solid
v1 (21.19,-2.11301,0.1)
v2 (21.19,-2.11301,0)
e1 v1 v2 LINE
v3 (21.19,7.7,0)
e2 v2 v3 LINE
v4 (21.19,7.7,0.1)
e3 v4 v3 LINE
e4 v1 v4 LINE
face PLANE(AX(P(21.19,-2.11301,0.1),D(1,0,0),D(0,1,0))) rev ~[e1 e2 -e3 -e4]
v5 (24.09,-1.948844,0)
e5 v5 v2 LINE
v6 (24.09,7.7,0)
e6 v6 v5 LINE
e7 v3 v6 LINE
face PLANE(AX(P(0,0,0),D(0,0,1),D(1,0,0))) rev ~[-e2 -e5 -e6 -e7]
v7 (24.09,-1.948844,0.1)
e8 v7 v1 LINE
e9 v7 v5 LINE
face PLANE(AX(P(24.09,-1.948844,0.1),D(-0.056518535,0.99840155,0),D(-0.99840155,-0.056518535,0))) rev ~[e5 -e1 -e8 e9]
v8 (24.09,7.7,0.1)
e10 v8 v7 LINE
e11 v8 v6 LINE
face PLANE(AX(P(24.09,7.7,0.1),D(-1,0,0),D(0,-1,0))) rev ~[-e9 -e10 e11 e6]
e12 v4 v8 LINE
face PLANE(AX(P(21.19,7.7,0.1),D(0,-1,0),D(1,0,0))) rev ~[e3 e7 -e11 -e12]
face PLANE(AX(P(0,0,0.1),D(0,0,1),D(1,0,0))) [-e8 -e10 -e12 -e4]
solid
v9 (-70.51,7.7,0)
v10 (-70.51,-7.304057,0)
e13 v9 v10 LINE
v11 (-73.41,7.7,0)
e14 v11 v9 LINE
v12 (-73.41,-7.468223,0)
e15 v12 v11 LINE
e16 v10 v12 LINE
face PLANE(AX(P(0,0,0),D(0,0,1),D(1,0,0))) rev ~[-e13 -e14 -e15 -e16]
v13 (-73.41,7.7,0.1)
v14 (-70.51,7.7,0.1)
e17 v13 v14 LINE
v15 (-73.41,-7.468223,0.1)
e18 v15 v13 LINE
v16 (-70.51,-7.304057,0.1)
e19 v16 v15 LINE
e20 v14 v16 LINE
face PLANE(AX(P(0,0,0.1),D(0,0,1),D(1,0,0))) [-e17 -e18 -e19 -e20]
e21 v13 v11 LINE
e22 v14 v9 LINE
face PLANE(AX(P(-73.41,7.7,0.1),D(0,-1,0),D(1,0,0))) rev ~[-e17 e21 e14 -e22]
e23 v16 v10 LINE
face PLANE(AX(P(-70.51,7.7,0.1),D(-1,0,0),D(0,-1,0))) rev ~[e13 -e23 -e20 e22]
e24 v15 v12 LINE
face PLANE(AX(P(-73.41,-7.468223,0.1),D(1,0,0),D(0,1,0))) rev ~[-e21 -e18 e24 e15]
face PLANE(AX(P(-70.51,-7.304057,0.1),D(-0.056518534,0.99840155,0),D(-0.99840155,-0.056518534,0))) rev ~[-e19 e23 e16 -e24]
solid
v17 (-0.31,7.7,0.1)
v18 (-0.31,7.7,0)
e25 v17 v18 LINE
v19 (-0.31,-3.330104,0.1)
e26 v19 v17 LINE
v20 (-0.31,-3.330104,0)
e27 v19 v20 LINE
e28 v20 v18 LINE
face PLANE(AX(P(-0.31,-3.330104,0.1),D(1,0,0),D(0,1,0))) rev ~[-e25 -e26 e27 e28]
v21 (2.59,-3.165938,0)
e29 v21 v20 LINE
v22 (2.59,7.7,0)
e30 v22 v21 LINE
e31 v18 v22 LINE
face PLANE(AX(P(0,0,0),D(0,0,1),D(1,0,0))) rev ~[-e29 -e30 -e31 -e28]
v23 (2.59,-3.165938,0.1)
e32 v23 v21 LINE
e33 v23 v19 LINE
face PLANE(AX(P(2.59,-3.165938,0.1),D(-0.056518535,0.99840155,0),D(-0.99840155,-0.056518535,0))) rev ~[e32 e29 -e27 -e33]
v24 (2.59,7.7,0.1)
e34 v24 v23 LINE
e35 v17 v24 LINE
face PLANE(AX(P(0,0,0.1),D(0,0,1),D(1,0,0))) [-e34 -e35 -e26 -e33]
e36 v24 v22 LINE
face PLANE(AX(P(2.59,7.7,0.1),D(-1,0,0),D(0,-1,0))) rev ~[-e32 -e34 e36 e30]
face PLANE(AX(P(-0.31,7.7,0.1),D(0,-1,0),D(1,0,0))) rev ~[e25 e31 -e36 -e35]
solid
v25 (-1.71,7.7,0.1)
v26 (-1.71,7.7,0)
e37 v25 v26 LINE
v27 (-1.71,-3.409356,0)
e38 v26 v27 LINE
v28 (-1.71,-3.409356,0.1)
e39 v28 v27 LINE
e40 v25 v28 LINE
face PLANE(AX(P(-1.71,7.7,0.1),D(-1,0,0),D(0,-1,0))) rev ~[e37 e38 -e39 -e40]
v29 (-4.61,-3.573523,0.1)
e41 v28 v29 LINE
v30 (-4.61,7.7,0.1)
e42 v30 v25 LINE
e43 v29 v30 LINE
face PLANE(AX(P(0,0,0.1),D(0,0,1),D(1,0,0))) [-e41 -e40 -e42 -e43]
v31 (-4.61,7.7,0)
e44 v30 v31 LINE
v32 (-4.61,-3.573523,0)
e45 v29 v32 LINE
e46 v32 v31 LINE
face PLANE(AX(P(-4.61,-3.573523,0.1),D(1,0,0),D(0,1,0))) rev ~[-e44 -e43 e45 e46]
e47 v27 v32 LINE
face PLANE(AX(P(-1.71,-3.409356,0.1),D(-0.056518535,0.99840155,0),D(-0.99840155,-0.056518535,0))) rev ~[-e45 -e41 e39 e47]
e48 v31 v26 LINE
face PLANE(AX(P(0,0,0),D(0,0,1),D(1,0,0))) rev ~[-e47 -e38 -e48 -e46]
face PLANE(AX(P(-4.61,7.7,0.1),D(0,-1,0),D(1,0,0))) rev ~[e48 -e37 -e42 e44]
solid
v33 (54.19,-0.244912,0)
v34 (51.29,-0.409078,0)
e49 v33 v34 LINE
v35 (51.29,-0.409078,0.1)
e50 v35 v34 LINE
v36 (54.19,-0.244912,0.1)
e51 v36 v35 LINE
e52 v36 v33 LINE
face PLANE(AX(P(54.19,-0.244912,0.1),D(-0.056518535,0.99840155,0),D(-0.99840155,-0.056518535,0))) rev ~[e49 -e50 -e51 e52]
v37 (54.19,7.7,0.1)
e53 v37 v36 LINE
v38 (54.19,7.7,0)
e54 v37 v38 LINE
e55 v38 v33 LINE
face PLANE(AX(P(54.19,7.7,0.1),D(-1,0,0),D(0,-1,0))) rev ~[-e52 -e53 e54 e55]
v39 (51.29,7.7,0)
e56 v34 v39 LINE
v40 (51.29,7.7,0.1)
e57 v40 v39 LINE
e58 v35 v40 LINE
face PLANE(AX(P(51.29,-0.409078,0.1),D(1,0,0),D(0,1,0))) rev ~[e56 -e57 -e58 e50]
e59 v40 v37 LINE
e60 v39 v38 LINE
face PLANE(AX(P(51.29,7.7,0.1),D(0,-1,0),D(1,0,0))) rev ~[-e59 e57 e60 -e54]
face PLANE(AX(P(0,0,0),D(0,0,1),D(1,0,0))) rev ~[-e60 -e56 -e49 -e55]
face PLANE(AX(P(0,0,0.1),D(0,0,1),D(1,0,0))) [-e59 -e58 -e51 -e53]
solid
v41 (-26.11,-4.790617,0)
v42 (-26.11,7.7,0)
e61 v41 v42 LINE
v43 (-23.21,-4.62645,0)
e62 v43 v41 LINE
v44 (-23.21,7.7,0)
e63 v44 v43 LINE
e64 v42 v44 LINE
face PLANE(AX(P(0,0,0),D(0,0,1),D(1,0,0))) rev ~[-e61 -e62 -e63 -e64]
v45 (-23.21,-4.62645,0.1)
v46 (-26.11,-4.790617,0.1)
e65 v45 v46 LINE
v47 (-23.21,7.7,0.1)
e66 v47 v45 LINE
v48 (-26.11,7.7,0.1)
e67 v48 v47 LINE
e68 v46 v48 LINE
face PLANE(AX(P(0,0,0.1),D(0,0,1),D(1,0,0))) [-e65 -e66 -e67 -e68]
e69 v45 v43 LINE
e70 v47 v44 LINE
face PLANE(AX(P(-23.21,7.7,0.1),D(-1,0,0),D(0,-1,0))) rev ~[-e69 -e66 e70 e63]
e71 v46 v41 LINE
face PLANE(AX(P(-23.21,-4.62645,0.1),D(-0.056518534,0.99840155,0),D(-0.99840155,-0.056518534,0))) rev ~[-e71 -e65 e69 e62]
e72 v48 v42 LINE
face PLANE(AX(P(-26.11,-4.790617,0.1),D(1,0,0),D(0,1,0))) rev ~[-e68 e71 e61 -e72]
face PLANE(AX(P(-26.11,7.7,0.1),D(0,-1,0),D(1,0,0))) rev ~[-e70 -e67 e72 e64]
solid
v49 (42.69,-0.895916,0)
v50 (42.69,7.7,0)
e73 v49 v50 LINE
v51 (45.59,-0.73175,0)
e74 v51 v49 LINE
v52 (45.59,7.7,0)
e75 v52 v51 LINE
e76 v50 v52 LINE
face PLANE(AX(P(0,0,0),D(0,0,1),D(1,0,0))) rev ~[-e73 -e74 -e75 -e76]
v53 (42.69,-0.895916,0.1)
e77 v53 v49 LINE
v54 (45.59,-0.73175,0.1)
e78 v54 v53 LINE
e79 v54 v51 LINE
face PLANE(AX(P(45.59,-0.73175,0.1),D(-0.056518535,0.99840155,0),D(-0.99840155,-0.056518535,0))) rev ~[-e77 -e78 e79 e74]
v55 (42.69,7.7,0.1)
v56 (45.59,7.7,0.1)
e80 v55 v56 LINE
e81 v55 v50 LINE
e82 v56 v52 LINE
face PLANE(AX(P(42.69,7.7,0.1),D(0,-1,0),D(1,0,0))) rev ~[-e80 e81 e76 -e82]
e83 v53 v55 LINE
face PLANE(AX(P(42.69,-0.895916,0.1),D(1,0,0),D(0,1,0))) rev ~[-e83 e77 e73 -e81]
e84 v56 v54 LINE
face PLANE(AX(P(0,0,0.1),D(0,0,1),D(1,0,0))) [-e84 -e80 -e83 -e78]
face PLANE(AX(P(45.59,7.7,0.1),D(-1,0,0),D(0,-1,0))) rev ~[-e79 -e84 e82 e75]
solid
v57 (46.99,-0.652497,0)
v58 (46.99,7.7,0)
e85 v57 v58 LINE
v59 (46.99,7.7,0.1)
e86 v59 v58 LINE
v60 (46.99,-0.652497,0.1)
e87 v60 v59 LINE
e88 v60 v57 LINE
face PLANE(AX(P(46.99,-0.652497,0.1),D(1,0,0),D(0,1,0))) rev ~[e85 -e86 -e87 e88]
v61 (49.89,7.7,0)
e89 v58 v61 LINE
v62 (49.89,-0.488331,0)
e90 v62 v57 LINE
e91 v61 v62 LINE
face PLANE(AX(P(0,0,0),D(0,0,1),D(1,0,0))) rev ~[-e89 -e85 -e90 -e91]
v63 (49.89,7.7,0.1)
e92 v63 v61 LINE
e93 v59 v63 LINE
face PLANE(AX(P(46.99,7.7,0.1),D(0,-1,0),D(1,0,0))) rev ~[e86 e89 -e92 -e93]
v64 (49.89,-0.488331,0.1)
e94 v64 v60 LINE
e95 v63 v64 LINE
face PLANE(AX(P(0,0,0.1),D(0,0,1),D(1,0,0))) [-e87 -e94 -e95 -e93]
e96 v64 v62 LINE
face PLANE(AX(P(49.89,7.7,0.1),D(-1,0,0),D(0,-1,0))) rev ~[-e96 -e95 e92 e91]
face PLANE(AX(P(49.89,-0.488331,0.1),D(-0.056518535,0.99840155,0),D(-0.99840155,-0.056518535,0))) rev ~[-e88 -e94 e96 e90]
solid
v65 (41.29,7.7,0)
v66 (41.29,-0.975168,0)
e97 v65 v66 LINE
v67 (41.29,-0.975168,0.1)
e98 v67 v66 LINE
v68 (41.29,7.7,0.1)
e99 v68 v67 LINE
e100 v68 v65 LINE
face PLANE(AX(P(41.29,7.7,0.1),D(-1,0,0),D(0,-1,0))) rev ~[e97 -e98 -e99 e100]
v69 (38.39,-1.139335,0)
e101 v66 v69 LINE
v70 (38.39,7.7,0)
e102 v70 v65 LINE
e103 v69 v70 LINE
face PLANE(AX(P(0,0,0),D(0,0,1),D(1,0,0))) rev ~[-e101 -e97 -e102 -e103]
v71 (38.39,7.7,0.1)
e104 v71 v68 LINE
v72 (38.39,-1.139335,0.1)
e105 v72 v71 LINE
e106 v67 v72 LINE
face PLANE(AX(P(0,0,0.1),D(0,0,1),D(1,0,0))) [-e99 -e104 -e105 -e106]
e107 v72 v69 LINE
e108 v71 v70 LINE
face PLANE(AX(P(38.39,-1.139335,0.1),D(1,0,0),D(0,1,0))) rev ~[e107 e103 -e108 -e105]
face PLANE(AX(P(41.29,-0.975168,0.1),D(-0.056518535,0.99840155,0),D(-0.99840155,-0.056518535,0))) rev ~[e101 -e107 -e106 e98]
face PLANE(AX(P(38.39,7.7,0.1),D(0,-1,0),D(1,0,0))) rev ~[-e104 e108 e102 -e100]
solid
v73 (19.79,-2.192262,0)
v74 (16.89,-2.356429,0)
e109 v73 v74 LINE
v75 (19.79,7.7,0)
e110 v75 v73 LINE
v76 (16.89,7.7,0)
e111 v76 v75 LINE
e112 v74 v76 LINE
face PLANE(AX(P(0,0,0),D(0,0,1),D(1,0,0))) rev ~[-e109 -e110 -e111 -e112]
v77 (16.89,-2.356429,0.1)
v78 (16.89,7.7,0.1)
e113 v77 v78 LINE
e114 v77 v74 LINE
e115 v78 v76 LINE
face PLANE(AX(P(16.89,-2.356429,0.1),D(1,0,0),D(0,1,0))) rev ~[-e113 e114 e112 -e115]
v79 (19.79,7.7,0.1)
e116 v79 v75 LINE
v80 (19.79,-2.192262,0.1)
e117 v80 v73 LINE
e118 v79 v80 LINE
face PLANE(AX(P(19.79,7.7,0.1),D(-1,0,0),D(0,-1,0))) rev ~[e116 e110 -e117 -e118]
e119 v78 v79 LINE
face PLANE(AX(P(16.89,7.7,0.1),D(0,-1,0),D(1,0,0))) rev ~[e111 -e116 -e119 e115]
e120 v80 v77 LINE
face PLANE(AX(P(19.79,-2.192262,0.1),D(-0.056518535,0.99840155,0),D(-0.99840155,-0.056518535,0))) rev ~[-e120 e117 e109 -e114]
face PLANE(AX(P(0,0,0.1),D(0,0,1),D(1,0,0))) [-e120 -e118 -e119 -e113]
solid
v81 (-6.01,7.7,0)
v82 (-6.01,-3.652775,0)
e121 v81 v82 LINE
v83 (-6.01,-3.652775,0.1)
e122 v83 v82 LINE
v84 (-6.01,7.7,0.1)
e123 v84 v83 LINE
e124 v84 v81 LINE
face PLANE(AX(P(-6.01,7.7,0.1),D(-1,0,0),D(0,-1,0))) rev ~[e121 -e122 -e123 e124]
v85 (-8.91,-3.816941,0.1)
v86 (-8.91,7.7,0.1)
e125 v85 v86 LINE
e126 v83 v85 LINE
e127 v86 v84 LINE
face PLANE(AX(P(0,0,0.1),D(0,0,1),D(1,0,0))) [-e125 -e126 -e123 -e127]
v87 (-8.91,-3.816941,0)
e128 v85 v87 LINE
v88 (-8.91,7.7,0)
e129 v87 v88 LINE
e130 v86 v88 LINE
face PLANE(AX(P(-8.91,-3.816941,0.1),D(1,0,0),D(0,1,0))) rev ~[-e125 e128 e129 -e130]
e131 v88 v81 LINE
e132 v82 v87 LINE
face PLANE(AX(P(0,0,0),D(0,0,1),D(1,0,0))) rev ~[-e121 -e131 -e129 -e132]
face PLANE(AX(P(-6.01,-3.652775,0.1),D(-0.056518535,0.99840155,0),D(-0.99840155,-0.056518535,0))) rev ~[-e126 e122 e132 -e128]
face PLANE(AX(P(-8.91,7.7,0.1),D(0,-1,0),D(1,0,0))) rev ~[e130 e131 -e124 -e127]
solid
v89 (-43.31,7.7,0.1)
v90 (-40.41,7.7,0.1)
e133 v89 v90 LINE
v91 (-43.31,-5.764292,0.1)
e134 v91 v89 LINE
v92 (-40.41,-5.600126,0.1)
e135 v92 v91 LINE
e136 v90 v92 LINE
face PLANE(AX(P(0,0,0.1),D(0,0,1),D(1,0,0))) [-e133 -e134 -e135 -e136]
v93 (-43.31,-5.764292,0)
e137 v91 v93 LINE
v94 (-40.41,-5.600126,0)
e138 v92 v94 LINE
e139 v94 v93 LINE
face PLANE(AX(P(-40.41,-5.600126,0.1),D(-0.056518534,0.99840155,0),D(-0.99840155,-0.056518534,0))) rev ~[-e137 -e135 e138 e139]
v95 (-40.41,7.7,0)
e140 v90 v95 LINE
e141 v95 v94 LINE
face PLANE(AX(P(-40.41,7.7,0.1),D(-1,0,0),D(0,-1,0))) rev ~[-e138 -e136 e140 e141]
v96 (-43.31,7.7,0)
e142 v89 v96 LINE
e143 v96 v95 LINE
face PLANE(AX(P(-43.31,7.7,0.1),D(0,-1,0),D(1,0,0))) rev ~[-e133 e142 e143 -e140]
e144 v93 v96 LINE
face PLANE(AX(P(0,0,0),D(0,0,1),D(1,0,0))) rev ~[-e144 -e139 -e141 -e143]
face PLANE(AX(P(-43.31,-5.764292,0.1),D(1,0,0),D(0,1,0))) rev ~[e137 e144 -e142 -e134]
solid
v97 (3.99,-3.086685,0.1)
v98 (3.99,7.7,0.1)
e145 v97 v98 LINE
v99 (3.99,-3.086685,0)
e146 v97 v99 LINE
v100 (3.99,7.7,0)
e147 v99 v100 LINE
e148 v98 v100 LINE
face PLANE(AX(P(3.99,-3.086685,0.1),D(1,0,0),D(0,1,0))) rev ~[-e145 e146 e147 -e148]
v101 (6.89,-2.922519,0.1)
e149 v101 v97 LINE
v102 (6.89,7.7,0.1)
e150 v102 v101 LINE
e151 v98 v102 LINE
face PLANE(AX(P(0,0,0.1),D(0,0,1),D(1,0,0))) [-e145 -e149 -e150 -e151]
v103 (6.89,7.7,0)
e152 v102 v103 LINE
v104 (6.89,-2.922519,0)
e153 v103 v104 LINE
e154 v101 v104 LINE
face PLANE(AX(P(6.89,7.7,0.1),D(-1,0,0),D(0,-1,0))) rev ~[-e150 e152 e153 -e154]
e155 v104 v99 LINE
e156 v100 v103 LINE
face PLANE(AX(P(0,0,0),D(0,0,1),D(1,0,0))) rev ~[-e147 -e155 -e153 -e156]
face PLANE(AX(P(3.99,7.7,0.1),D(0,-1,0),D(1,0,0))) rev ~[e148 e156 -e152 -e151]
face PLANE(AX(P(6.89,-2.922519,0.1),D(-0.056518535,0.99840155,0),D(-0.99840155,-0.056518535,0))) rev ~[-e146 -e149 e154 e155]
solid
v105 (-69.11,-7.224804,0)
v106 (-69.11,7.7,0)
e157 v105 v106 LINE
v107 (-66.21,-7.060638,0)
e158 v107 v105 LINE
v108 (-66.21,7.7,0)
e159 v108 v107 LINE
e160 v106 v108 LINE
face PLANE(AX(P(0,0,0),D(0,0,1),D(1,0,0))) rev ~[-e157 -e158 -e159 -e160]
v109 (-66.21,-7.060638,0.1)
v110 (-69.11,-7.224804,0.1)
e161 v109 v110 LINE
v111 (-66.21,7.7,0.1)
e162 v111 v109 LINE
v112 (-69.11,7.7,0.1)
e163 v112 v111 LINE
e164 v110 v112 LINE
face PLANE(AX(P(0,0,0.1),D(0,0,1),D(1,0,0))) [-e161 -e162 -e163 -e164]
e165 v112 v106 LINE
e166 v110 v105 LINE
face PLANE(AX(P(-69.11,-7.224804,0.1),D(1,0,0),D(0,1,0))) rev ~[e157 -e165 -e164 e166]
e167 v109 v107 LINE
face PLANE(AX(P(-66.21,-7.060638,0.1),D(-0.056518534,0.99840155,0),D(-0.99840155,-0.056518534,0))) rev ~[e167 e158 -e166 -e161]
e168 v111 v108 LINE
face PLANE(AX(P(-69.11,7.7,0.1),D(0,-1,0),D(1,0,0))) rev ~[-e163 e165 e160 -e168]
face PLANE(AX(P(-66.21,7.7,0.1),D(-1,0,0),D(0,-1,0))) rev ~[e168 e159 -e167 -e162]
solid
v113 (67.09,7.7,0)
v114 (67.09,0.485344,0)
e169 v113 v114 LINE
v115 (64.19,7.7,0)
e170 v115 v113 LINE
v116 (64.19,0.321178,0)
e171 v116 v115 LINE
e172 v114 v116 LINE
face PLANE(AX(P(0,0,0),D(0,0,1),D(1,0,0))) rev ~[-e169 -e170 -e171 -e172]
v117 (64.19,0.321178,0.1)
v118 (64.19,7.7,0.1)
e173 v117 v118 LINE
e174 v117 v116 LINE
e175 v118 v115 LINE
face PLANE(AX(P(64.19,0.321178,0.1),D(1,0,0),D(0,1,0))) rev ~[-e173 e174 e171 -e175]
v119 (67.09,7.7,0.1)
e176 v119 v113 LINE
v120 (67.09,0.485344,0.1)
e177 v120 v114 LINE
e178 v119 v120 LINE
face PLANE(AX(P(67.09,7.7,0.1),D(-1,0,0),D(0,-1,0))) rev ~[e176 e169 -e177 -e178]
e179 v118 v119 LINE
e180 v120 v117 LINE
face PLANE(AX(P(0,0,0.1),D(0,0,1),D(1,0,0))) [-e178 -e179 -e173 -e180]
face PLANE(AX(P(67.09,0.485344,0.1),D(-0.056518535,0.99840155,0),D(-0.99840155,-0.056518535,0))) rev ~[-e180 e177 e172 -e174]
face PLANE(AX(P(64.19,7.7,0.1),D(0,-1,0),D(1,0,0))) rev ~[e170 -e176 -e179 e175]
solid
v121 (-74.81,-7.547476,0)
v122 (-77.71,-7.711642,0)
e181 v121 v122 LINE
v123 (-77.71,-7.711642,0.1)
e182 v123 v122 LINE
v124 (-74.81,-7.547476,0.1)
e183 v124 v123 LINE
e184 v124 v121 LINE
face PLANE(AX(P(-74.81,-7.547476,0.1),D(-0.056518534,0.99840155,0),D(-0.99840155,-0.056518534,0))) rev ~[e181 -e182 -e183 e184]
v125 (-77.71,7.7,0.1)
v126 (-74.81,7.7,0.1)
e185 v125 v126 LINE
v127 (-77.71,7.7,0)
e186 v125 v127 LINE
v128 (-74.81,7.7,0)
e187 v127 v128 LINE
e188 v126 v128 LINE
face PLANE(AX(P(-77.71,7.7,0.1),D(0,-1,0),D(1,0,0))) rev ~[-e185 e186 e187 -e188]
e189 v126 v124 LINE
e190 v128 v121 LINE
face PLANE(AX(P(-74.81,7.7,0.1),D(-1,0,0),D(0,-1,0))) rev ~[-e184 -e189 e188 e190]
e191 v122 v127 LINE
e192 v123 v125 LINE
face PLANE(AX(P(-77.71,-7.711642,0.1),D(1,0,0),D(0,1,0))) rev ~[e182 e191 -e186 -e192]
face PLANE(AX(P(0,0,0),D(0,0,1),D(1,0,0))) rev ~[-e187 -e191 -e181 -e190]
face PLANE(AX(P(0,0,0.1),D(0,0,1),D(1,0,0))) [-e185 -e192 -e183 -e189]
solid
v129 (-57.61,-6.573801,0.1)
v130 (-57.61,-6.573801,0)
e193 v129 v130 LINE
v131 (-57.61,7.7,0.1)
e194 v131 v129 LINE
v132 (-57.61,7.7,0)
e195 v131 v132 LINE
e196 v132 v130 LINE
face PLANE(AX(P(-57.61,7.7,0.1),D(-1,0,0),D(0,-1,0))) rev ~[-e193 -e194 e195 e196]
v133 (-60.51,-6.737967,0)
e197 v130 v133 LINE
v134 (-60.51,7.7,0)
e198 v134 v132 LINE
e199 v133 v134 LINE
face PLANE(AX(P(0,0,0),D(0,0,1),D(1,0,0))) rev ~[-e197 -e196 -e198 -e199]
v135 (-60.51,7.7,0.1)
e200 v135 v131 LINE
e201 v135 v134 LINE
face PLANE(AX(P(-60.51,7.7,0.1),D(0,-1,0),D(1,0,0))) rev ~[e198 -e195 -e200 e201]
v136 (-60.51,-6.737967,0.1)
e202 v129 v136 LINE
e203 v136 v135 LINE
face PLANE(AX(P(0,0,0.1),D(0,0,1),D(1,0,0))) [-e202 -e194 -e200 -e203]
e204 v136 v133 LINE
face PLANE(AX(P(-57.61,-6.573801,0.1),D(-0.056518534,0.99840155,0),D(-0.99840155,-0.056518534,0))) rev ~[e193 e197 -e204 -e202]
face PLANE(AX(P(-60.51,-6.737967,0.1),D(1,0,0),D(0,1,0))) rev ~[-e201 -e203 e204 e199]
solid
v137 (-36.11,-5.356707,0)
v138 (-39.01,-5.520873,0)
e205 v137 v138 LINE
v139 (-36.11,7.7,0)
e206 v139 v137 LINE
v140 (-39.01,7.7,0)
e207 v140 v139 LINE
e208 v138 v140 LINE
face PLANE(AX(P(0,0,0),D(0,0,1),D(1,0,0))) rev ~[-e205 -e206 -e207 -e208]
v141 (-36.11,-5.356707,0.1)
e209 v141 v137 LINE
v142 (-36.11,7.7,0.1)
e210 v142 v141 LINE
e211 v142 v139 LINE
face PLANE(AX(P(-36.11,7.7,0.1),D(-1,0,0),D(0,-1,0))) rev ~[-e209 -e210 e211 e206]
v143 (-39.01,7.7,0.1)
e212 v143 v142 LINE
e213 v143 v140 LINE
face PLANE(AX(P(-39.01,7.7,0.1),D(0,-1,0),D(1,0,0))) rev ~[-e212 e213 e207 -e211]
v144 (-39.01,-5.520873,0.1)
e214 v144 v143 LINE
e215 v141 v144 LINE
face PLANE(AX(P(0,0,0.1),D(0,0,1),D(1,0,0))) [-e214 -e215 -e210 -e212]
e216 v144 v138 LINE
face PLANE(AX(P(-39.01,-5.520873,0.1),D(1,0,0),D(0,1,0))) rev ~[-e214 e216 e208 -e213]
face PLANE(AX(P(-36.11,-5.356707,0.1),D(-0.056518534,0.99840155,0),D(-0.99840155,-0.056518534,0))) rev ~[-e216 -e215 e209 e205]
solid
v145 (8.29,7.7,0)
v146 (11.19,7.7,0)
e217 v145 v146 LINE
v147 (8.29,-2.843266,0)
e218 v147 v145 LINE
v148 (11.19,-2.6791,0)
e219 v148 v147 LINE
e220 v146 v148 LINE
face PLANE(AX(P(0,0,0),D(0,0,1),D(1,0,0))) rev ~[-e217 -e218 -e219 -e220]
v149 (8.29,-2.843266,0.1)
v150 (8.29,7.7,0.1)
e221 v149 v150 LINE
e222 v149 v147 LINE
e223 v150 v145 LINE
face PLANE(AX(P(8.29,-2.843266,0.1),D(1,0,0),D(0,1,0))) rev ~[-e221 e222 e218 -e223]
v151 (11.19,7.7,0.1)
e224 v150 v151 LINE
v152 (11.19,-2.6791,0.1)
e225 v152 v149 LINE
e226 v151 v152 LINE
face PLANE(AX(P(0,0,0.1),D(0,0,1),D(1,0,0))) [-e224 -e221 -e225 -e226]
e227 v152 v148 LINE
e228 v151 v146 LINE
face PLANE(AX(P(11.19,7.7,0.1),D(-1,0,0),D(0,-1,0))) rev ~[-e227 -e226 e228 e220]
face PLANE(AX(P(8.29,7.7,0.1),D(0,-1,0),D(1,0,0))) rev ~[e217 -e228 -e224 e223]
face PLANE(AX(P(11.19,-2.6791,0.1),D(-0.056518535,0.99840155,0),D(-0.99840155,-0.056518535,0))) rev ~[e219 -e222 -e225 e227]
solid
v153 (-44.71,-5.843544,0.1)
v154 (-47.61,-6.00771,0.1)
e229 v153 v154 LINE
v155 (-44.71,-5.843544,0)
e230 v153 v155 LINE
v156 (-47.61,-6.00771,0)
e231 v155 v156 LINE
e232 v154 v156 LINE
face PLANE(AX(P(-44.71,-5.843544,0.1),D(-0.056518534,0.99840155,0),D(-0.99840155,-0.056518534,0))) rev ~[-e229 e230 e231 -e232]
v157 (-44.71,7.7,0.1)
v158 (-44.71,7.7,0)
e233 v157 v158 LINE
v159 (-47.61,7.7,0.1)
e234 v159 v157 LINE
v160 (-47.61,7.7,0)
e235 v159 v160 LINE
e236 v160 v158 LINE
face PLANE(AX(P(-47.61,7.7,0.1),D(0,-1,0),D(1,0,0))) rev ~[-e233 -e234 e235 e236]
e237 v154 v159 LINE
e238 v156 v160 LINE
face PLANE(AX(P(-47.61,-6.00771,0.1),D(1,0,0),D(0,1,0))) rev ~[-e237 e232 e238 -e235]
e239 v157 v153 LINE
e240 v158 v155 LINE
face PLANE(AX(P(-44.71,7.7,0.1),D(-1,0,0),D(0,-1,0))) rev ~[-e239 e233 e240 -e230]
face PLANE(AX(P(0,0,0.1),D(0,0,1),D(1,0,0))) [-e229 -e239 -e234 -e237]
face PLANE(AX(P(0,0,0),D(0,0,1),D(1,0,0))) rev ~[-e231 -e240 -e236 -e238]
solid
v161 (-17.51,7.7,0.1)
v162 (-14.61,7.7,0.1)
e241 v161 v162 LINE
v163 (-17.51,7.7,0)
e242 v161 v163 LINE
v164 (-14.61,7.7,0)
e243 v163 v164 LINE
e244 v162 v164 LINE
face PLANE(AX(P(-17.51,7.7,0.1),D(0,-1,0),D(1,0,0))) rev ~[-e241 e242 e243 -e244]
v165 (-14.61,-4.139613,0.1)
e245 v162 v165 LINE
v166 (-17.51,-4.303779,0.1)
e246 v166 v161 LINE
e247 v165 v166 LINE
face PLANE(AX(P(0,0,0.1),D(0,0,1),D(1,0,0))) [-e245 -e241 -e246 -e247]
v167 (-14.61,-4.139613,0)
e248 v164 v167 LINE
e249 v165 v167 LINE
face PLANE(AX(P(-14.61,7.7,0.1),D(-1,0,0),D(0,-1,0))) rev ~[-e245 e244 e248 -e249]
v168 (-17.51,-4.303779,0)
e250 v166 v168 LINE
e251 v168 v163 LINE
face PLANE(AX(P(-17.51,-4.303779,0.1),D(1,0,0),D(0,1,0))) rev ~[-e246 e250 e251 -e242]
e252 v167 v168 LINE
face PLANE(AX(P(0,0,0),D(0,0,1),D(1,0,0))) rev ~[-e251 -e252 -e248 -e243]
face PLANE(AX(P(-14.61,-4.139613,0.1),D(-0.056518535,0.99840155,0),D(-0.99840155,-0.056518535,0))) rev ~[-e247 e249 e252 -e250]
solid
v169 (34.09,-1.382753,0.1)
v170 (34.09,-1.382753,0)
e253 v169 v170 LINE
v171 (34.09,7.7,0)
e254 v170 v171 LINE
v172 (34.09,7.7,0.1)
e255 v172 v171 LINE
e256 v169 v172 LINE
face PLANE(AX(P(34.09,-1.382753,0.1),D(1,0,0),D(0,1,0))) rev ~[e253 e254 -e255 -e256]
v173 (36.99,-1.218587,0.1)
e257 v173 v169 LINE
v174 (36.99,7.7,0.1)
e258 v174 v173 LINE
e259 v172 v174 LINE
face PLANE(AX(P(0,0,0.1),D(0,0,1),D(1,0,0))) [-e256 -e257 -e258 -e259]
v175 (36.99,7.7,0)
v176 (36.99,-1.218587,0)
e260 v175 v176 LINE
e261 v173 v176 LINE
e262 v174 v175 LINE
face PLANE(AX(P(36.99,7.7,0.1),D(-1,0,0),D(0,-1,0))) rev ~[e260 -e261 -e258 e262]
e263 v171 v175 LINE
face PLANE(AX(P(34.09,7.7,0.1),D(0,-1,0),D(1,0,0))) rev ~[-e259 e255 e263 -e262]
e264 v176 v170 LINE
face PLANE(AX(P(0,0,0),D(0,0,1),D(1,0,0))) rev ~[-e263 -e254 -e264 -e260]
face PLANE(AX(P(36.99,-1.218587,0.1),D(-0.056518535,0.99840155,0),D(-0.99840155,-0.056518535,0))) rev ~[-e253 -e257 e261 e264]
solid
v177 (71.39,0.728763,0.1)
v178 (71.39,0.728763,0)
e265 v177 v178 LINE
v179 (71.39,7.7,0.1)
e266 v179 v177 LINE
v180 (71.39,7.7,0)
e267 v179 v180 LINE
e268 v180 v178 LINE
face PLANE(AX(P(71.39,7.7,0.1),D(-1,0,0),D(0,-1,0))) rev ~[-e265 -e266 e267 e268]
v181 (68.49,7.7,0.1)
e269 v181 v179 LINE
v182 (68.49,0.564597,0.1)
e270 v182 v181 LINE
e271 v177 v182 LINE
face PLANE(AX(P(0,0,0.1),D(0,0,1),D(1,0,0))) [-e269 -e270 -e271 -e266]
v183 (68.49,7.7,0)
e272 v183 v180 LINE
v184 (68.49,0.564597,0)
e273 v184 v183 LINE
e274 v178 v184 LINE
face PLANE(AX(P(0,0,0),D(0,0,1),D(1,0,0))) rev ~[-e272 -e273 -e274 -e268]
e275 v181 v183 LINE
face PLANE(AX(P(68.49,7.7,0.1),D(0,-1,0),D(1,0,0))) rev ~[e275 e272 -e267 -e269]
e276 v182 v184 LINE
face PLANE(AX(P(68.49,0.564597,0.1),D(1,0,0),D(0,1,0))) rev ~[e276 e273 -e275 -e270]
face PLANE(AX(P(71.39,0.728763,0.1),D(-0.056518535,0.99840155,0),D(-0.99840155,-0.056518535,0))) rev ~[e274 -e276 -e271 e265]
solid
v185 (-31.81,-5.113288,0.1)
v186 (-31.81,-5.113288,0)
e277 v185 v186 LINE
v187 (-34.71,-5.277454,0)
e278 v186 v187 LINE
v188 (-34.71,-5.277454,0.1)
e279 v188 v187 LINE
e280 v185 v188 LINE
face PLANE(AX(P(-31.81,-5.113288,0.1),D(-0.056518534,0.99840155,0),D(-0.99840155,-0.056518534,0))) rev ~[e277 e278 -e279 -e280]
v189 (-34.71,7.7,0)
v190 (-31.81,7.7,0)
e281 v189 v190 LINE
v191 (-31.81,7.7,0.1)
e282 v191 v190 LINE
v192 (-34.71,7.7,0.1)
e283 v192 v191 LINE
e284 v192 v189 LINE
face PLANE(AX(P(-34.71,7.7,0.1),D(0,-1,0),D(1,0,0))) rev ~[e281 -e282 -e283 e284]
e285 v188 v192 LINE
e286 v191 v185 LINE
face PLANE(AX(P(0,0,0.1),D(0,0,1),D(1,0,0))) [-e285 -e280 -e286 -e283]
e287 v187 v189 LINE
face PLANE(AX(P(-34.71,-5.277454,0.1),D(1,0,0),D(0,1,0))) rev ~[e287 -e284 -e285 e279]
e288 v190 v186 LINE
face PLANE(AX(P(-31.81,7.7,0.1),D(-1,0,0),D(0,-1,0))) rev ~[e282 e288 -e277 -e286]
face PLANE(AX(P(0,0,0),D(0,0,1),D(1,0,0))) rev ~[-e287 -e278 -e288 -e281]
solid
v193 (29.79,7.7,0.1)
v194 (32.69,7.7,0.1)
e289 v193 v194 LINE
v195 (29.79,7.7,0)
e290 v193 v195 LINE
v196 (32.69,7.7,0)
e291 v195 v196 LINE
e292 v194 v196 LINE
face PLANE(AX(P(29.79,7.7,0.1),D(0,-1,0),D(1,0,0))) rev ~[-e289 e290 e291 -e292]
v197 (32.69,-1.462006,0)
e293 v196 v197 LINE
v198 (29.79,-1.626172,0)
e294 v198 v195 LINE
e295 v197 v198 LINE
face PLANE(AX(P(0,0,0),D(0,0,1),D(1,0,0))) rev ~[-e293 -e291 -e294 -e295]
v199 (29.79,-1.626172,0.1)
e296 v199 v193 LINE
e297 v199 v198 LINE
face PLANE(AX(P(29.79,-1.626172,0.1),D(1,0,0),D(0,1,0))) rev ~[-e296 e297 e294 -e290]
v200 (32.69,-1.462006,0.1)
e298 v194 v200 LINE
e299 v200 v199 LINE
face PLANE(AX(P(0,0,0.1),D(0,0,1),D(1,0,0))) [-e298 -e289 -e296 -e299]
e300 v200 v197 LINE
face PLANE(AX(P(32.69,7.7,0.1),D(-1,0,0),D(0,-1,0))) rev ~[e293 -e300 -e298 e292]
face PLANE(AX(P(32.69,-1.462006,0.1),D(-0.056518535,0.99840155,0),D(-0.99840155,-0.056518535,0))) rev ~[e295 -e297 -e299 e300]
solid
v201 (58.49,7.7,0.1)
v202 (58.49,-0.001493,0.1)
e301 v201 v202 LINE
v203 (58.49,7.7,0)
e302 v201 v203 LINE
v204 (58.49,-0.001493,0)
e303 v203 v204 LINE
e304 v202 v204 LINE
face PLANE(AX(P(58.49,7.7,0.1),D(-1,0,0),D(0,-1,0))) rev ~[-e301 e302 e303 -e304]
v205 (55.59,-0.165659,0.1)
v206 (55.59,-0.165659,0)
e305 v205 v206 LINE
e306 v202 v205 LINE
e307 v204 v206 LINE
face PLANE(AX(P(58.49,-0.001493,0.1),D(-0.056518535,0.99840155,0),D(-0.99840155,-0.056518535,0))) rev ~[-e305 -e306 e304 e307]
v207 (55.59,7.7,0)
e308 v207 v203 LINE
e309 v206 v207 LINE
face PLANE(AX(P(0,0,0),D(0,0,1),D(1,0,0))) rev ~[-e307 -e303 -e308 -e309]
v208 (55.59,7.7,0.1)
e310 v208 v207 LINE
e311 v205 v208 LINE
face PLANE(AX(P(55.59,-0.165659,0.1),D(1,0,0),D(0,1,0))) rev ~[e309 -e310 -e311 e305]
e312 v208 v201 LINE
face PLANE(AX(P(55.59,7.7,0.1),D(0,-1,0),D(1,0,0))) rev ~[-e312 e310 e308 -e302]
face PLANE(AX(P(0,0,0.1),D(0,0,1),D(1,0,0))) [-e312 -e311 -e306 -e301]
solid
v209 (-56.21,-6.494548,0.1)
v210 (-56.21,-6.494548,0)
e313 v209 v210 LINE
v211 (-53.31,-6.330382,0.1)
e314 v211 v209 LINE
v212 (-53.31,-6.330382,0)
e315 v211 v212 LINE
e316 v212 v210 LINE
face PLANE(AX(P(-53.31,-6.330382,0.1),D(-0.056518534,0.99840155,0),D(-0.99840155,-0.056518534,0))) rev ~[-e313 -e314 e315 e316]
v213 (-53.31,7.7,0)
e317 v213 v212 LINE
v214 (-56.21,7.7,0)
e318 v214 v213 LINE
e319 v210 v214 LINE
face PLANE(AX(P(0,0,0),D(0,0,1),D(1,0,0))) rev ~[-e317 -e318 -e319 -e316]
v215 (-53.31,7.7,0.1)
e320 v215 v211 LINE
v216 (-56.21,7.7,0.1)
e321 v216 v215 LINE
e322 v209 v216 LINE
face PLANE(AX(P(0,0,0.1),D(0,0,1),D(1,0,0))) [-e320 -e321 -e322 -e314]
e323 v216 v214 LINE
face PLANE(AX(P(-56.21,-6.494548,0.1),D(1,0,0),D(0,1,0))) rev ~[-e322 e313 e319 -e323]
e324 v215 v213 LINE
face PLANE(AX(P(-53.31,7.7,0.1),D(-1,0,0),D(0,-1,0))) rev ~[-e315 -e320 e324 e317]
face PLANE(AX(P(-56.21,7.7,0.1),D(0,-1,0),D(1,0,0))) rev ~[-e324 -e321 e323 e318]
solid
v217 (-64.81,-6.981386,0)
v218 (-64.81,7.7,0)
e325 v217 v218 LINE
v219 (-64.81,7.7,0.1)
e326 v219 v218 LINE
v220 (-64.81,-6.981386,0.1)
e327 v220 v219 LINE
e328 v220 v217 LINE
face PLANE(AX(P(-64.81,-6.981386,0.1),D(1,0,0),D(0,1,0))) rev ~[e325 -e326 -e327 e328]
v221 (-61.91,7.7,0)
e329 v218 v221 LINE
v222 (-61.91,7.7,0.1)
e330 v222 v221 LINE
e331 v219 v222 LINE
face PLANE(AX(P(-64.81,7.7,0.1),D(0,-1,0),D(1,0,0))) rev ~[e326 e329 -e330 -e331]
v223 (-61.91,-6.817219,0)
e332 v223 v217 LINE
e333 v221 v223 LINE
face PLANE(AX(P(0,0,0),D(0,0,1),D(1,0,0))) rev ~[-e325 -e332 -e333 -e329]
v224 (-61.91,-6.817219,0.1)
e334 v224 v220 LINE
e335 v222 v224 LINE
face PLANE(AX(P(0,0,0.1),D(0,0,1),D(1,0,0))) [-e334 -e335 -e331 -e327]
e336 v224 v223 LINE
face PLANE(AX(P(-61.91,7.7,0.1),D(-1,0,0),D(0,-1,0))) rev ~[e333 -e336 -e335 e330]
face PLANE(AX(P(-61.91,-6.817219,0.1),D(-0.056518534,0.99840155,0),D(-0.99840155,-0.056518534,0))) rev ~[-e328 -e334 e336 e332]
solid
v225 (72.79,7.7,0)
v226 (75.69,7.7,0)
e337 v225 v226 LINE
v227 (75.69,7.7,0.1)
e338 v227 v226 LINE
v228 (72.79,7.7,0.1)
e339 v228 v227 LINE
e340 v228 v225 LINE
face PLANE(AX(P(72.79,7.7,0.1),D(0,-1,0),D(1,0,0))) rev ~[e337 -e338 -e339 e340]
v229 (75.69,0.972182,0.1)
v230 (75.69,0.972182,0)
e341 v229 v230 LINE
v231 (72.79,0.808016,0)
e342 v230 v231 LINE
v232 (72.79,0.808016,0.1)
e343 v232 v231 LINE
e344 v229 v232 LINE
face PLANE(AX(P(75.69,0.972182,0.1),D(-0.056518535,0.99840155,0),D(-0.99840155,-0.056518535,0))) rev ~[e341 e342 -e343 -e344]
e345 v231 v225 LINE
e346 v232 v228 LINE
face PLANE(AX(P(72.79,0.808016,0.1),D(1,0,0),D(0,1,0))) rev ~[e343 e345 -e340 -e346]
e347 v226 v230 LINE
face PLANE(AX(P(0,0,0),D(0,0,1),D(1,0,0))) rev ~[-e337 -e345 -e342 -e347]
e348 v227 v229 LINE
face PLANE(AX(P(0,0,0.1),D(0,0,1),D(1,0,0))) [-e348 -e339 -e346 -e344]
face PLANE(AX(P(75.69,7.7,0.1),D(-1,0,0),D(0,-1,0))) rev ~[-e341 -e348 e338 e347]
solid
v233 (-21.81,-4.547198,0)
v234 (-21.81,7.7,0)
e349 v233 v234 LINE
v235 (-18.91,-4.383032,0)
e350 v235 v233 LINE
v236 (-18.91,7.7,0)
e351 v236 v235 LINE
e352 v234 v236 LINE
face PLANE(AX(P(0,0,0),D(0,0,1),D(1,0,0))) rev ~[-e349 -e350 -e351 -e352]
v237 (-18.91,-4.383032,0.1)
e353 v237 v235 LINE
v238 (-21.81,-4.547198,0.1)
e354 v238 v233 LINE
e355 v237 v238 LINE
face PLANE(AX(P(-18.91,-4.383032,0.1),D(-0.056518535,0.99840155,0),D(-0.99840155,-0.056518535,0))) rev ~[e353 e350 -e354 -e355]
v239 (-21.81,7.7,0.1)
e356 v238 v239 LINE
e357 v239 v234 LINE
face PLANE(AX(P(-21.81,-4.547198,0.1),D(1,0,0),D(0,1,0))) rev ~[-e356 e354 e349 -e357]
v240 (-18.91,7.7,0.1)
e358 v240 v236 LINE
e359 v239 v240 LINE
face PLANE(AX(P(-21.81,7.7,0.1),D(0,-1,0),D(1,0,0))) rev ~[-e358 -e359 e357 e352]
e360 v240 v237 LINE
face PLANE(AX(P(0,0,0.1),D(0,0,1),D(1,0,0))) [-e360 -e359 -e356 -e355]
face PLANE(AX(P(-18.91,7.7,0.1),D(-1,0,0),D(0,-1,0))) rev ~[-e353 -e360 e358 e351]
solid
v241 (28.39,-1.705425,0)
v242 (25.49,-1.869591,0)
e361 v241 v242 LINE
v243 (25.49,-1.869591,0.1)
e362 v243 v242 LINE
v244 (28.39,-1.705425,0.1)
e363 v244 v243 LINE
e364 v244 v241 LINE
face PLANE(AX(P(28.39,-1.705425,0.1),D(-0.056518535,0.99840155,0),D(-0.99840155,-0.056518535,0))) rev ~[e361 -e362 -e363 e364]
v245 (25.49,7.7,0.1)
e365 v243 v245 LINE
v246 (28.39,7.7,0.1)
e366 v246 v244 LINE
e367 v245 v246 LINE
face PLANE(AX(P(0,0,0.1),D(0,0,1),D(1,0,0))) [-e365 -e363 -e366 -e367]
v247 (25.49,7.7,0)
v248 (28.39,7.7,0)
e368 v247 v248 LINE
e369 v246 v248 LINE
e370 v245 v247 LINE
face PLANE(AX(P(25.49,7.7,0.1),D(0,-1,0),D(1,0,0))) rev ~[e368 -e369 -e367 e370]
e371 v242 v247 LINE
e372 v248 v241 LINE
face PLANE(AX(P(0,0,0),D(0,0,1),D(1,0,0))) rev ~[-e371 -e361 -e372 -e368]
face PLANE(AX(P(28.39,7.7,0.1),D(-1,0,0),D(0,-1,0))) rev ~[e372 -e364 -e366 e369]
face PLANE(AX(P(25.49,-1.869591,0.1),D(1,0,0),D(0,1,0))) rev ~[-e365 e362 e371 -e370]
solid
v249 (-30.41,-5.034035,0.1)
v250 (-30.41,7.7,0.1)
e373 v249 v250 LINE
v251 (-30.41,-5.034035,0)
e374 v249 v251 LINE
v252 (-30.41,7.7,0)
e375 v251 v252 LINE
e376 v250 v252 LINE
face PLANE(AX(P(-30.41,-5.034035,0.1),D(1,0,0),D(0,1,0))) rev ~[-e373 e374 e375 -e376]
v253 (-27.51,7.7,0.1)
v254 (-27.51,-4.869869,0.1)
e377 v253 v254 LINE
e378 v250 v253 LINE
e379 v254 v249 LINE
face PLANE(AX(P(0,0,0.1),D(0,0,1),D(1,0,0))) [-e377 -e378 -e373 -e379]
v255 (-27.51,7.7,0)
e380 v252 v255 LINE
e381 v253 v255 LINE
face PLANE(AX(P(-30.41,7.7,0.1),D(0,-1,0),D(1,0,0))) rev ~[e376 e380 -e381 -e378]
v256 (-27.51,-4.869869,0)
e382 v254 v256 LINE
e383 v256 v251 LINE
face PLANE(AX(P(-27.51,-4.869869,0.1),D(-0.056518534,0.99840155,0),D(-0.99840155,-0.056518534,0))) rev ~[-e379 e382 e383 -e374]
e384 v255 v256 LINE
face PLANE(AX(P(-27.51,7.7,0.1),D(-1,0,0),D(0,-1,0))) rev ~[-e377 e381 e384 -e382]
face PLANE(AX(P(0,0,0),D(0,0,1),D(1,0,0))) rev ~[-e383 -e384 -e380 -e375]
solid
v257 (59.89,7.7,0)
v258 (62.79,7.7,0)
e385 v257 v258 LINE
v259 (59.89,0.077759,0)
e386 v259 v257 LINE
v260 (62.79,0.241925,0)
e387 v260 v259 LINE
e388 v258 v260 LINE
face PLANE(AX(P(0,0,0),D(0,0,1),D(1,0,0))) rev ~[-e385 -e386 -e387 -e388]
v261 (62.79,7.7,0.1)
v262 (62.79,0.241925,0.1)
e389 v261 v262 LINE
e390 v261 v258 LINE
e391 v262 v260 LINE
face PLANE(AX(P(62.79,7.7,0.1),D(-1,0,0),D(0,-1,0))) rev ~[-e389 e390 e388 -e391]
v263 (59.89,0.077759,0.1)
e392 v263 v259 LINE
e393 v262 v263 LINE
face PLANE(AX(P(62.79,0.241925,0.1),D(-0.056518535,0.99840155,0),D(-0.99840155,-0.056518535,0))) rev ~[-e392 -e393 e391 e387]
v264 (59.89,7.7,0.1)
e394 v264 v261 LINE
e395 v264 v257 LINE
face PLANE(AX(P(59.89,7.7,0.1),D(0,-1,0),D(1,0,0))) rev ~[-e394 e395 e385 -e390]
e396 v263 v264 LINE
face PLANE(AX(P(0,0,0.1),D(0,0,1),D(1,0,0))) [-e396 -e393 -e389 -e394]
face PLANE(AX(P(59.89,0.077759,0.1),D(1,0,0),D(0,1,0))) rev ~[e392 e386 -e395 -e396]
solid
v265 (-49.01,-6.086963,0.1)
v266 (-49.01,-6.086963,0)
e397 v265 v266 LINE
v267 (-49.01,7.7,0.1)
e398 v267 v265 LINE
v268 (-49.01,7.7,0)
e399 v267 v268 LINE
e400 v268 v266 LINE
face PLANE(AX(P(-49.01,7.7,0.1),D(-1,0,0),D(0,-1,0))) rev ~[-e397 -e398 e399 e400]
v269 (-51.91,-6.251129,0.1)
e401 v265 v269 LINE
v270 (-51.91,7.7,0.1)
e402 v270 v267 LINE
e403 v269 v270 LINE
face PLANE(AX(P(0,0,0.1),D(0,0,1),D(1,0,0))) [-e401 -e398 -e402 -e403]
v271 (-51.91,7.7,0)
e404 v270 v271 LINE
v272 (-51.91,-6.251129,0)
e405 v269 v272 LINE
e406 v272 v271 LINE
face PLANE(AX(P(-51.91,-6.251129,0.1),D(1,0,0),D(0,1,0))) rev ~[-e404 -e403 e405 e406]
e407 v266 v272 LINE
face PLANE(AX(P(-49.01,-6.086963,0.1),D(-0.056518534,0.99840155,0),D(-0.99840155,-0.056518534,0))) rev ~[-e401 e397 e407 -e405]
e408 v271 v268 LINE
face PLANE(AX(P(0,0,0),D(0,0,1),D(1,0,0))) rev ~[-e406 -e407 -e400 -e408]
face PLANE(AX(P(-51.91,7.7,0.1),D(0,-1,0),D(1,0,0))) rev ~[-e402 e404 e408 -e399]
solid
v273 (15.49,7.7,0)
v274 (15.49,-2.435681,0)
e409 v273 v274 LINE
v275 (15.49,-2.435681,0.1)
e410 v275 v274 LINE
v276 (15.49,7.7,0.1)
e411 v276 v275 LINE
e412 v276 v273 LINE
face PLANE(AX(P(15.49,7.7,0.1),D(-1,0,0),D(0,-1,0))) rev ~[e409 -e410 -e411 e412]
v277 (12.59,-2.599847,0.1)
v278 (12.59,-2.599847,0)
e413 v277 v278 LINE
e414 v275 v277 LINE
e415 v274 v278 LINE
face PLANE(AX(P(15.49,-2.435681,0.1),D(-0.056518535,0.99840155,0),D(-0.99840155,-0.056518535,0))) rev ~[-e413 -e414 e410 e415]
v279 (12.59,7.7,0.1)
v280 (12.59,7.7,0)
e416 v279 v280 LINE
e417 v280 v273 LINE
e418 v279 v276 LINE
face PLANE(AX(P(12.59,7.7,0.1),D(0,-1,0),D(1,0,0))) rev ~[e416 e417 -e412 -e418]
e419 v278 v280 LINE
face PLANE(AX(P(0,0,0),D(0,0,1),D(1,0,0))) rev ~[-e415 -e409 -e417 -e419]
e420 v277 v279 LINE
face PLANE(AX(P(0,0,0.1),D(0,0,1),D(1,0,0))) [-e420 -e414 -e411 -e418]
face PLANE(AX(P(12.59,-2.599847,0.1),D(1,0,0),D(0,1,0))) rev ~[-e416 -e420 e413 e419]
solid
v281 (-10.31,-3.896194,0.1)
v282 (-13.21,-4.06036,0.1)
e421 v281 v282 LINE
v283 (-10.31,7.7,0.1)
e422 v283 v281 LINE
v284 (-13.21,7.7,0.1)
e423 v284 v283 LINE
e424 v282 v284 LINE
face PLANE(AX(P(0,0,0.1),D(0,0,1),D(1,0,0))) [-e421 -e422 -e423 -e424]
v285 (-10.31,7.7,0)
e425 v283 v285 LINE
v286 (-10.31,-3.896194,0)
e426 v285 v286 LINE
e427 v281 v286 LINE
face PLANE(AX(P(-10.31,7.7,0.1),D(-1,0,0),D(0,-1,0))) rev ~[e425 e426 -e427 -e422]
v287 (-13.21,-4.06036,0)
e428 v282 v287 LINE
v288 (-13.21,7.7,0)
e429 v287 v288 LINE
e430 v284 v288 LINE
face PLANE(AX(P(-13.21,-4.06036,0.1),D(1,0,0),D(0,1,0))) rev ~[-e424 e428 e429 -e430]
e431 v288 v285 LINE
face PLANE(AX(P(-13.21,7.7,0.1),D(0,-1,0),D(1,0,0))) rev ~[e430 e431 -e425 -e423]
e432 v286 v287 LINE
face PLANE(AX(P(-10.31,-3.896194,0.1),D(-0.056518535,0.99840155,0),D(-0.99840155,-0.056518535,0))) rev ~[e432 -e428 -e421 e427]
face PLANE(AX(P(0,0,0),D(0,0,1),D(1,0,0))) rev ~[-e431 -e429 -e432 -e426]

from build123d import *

# Parameters (mm, degrees)
SKETCH1_W           = 178.5
SKETCH1_H           = 19
BOSS_EXTRUDE1_DEPTH = 0.1
SKETCH2_W           = 214.462169904
SKETCH2_H           = 58.553279971
CUT_EXTRUDE1_DEPTH  = 10


with BuildPart() as part:
    # Sketch1 → Boss-Extrude1 (new body)
    with BuildSketch(Plane.XY):
        Rectangle(SKETCH1_W, SKETCH1_H)
    extrude(amount=BOSS_EXTRUDE1_DEPTH)

    # Sketch2 → Cut-Extrude1 (cut)
    with BuildSketch(Plane.XY.offset(0.1)):
        with Locations((2.468770954, -3.863989357)):
            Rectangle(SKETCH2_W, SKETCH2_H)
        Polygon((-77.71, 7.7), (-74.81, 7.7), (-74.81, -7.547475845), (-77.71, -7.711642006), align=None, mode=Mode.SUBTRACT)
        Polygon((-73.41, 7.7), (-70.51, 7.7), (-70.51, -7.304057054), (-73.41, -7.468223215), align=None, mode=Mode.SUBTRACT)
        Polygon((-69.11, 7.7), (-66.21, 7.7), (-66.21, -7.060638263), (-69.11, -7.224804424), align=None, mode=Mode.SUBTRACT)
        Polygon((-64.81, 7.7), (-61.91, 7.7), (-61.91, -6.817219472), (-64.81, -6.981385633), align=None, mode=Mode.SUBTRACT)
        Polygon((-60.51, 7.7), (-57.61, 7.7), (-57.61, -6.573800681), (-60.51, -6.737966842), align=None, mode=Mode.SUBTRACT)
        Polygon((-56.21, 7.7), (-53.31, 7.7), (-53.31, -6.33038189), (-56.21, -6.494548051), align=None, mode=Mode.SUBTRACT)
        Polygon((-51.91, 7.7), (-49.01, 7.7), (-49.01, -6.086963099), (-51.91, -6.25112926), align=None, mode=Mode.SUBTRACT)
        Polygon((-47.61, 7.7), (-44.71, 7.7), (-44.71, -5.843544308), (-47.61, -6.007710469), align=None, mode=Mode.SUBTRACT)
        Polygon((-43.31, 7.7), (-40.41, 7.7), (-40.41, -5.600125517), (-43.31, -5.764291678), align=None, mode=Mode.SUBTRACT)
        Polygon((-39.01, 7.7), (-36.11, 7.7), (-36.11, -5.356706726), (-39.01, -5.520872887), align=None, mode=Mode.SUBTRACT)
        Polygon((-34.71, 7.7), (-31.81, 7.7), (-31.81, -5.113287935), (-34.71, -5.277454096), align=None, mode=Mode.SUBTRACT)
        Polygon((-30.41, 7.7), (-27.51, 7.7), (-27.51, -4.869869144), (-30.41, -5.034035305), align=None, mode=Mode.SUBTRACT)
        Polygon((-26.11, 7.7), (-23.21, 7.7), (-23.21, -4.626450353), (-26.11, -4.790616514), align=None, mode=Mode.SUBTRACT)
        Polygon((-21.81, 7.7), (-18.91, 7.7), (-18.91, -4.383031561), (-21.81, -4.547197723), align=None, mode=Mode.SUBTRACT)
        Polygon((-17.51, 7.7), (-14.61, 7.7), (-14.61, -4.13961277), (-17.51, -4.303778932), align=None, mode=Mode.SUBTRACT)
        Polygon((-13.21, 7.7), (-10.31, 7.7), (-10.31, -3.896193979), (-13.21, -4.060360141), align=None, mode=Mode.SUBTRACT)
        Polygon((-8.91, 7.7), (-6.01, 7.7), (-6.01, -3.652775188), (-8.91, -3.81694135), align=None, mode=Mode.SUBTRACT)
        Polygon((-4.61, 7.7), (-1.71, 7.7), (-1.71, -3.409356397), (-4.61, -3.573522559), align=None, mode=Mode.SUBTRACT)
        Polygon((-0.31, 7.7), (2.59, 7.7), (2.59, -3.165937606), (-0.31, -3.330103768), align=None, mode=Mode.SUBTRACT)
        Polygon((3.99, 7.7), (6.89, 7.7), (6.89, -2.922518815), (3.99, -3.086684977), align=None, mode=Mode.SUBTRACT)
        Polygon((8.29, 7.7), (11.19, 7.7), (11.19, -2.679100024), (8.29, -2.843266186), align=None, mode=Mode.SUBTRACT)
        Polygon((12.59, 7.7), (15.49, 7.7), (15.49, -2.435681233), (12.59, -2.599847395), align=None, mode=Mode.SUBTRACT)
        Polygon((16.89, 7.7), (19.79, 7.7), (19.79, -2.192262442), (16.89, -2.356428604), align=None, mode=Mode.SUBTRACT)
        Polygon((21.19, 7.7), (24.09, 7.7), (24.09, -1.948843651), (21.19, -2.113009813), align=None, mode=Mode.SUBTRACT)
        Polygon((25.49, 7.7), (28.39, 7.7), (28.39, -1.70542486), (25.49, -1.869591022), align=None, mode=Mode.SUBTRACT)
        Polygon((29.79, 7.7), (32.69, 7.7), (32.69, -1.462006069), (29.79, -1.626172231), align=None, mode=Mode.SUBTRACT)
        Polygon((34.09, 7.7), (36.99, 7.7), (36.99, -1.218587278), (34.09, -1.38275344), align=None, mode=Mode.SUBTRACT)
        Polygon((38.39, 7.7), (41.29, 7.7), (41.29, -0.975168487), (38.39, -1.139334649), align=None, mode=Mode.SUBTRACT)
        Polygon((42.69, 7.7), (45.59, 7.7), (45.59, -0.731749696), (42.69, -0.895915858), align=None, mode=Mode.SUBTRACT)
        Polygon((46.99, 7.7), (49.89, 7.7), (49.89, -0.488330905), (46.99, -0.652497067), align=None, mode=Mode.SUBTRACT)
        Polygon((51.29, 7.7), (54.19, 7.7), (54.19, -0.244912114), (51.29, -0.409078276), align=None, mode=Mode.SUBTRACT)
        Polygon((55.59, 7.7), (58.49, 7.7), (58.49, -0.001493323), (55.59, -0.165659485), align=None, mode=Mode.SUBTRACT)
        Polygon((59.89, 7.7), (62.79, 7.7), (62.79, 0.241925468), (59.89, 0.077759306), align=None, mode=Mode.SUBTRACT)
        Polygon((64.19, 7.7), (67.09, 7.7), (67.09, 0.485344259), (64.19, 0.321178097), align=None, mode=Mode.SUBTRACT)
        Polygon((68.49, 7.7), (71.39, 7.7), (71.39, 0.72876305), (68.49, 0.564596888), align=None, mode=Mode.SUBTRACT)
        Polygon((72.79, 7.7), (75.69, 7.7), (75.69, 0.972181841), (72.79, 0.808015679), align=None, mode=Mode.SUBTRACT)
    extrude(amount=-CUT_EXTRUDE1_DEPTH, mode=Mode.SUBTRACT)


solid = part.part
